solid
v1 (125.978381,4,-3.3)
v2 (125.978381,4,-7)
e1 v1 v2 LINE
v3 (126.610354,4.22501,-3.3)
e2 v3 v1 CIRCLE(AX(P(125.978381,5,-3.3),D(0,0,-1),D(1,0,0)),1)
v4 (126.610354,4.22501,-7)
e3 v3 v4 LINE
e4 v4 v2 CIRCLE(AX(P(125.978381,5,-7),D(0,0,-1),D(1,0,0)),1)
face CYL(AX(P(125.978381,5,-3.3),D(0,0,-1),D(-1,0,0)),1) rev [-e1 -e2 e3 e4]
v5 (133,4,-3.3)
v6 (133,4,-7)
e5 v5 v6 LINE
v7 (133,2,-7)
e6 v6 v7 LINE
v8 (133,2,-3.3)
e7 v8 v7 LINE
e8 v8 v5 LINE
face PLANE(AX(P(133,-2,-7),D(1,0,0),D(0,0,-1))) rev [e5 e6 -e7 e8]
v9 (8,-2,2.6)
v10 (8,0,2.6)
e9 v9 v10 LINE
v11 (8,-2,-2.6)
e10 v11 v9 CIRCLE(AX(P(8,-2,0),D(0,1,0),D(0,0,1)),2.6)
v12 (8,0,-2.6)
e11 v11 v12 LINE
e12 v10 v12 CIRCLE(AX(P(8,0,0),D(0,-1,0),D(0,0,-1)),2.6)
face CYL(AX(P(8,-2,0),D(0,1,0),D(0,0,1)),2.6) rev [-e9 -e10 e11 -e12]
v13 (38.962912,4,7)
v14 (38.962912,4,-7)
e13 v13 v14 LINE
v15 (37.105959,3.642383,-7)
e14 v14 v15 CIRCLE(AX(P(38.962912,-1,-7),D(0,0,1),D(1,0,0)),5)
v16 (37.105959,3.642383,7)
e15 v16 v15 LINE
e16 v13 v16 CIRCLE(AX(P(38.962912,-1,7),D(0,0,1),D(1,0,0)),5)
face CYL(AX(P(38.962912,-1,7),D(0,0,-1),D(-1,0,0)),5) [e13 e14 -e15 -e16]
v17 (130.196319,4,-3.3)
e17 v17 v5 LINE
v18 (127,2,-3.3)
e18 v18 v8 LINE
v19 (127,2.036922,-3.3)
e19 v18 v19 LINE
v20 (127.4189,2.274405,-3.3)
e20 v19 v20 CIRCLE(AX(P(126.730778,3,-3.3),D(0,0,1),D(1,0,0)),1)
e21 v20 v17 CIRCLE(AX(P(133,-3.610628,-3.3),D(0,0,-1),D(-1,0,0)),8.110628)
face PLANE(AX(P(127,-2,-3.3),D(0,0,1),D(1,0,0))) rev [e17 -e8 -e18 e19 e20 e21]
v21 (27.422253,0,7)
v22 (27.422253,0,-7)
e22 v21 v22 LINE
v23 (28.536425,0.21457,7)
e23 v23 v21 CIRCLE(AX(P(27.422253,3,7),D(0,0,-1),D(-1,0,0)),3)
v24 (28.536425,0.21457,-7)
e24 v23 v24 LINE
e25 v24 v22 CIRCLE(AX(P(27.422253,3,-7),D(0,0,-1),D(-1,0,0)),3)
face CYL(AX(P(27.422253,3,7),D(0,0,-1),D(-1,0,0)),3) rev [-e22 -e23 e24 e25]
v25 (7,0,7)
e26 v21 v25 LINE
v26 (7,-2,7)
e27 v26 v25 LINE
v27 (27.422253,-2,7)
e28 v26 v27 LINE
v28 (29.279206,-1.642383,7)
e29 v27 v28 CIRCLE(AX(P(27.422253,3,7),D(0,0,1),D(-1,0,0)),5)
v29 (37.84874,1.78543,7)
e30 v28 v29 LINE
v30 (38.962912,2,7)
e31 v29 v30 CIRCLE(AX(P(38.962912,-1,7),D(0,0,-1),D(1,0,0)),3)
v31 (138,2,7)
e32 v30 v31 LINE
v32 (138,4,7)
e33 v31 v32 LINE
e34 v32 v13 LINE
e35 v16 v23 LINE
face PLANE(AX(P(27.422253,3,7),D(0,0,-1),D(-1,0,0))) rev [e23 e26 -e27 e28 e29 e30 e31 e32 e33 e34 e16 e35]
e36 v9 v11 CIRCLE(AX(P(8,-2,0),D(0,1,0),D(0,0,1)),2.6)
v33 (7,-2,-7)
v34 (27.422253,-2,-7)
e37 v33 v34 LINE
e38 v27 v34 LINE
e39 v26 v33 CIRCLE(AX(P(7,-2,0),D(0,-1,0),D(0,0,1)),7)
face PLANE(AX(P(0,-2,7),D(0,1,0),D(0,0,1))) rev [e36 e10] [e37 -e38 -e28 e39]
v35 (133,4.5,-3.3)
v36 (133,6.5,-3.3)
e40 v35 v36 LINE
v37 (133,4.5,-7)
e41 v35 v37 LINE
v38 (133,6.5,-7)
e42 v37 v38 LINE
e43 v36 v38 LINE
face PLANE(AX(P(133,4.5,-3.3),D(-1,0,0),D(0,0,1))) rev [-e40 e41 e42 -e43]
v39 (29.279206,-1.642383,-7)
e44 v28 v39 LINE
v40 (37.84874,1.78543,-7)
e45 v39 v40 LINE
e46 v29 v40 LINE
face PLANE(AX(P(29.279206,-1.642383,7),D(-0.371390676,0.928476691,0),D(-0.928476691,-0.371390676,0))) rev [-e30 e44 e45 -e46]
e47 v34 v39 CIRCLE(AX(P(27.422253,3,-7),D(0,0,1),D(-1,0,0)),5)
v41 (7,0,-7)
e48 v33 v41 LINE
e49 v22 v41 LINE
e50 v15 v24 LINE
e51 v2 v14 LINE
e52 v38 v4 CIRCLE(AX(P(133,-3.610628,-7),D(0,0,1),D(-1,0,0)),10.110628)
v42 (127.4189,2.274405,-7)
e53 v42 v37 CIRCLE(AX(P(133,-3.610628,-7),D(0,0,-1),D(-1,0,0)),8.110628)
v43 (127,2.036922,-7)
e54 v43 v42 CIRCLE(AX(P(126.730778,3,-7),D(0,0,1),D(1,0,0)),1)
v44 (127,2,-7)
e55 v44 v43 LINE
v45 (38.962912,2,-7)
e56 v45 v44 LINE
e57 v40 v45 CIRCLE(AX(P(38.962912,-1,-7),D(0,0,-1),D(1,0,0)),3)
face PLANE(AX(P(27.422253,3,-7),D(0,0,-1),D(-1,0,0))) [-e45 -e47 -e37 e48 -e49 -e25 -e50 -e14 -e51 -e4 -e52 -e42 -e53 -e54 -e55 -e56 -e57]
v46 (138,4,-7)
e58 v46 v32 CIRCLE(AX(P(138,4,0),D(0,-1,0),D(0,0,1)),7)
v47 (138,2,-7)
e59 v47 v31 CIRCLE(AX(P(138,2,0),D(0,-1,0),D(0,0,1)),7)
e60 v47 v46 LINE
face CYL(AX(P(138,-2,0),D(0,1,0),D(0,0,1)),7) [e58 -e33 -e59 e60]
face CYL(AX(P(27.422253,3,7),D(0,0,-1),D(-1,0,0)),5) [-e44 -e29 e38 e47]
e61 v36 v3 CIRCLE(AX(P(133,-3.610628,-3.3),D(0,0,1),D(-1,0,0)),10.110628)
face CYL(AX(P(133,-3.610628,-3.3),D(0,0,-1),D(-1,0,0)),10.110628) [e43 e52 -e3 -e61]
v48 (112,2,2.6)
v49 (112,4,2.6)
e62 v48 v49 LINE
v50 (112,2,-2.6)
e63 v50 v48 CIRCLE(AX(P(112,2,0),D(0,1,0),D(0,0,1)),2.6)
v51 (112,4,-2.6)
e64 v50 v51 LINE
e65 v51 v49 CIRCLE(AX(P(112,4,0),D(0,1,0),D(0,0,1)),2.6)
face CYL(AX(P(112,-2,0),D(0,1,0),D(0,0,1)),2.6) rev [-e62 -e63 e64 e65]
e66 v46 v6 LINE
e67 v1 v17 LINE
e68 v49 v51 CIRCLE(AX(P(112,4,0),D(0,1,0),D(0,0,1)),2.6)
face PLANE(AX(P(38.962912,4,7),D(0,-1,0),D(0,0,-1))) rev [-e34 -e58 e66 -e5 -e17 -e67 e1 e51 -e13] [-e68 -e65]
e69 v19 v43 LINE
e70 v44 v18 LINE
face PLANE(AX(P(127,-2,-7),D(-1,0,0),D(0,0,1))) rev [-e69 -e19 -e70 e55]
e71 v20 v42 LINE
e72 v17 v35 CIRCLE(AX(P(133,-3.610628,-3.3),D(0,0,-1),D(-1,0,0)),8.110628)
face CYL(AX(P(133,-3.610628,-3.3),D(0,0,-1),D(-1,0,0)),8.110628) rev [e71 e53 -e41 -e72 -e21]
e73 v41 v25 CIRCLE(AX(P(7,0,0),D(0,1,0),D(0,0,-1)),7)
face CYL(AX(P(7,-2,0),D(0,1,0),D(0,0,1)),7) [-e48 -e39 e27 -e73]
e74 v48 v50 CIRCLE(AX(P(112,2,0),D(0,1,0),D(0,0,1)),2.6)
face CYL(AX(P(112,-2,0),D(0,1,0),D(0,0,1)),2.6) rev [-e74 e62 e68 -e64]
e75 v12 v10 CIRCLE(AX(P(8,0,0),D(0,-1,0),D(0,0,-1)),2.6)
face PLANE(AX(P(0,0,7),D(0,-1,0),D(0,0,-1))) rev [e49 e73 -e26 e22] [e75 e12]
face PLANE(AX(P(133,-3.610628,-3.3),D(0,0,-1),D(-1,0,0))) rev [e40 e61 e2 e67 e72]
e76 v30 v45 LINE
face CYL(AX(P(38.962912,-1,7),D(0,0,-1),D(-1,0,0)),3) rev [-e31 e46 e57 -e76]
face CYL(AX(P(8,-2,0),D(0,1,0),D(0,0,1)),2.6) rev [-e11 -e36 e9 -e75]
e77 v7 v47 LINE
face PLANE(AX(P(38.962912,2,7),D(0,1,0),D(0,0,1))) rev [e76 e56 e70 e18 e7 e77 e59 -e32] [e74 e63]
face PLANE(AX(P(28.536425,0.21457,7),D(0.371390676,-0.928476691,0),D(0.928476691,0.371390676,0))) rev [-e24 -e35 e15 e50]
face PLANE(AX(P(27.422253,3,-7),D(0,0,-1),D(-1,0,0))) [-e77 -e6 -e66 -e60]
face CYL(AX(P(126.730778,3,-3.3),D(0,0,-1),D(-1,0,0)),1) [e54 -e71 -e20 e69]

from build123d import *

# Parameters (mm, degrees)
EXTRUDE1_DEPTH      = 7
EXTRUDE2_DEPTH      = 146.223964964
EXTRUDE2_DEPTH_BACK = 146.223964964
SKETCH2_R           = 2.6
SKETCH5_W           = 6
SKETCH5_H           = 3.7
EXTRUDE5_DEPTH      = 146.292807805
EXTRUDE6_DEPTH      = 3.7


with BuildPart() as part:
    # Sketch1 → Extrude1 (new, symmetric)
    with BuildSketch(Plane.XY):
        with BuildLine():
            Line((0, 0), (27.422252789, 0))
            ThreePointArc((27.422252789, 0), (27.989575353, 0.05413084), (28.536424818, 0.214569927))
            Line((28.536424818, 0.214569927), (37.105958636, 3.642383454))
            ThreePointArc((37.105958636, 3.642383454), (38.017374412, 3.909781934), (38.962912018, 4))
            Line((38.962912018, 4), (145, 4))
            Line((145, 4), (145, 2))
            Line((145, 2), (38.962912018, 2))
            ThreePointArc((38.962912018, 2), (38.395589454, 1.94586916), (37.848739989, 1.785430073))
            Line((37.848739989, 1.785430073), (29.279206171, -1.642383454))
            ThreePointArc((29.279206171, -1.642383454), (28.367790395, -1.909781934), (27.422252789, -2))
            Line((27.422252789, -2), (0, -2))
            Line((0, -2), (0, 0))
        make_face()
    extrude(amount=EXTRUDE1_DEPTH, both=True)

    # Sketch2 → Extrude2 (cut, two sides: drawn at the far end of the back side and taken through both)
    with BuildSketch(Plane(origin=(0, 0, 0), x_dir=(1, 0, 0), z_dir=(0, 1, 0)).offset(-EXTRUDE2_DEPTH_BACK)):
        with Locations(Location((8, 0, 0), (0, 0, 270))):
            Circle(SKETCH2_R)
        with Locations(Location((112, 0, 0), (0, 0, 270))):
            Circle(SKETCH2_R)
        with BuildLine():
            Line((138, 7), (138, 13.502314884))
            Line((138, 13.502314884), (156.33198023, 13.502314884))
            Line((156.33198023, 13.502314884), (156.33198023, -14.26269046))
            Line((156.33198023, -14.26269046), (138, -14.26269046))
            Line((138, -14.26269046), (138, -7))
            ThreePointArc((138, -7), (145, 0), (138, 7))
        make_face()
        with BuildLine():
            Line((7, 7), (7, 12.663603668))
            Line((7, 12.663603668), (-7.097085647, 12.663603668))
            Line((-7.097085647, 12.663603668), (-7.097085647, -11.053510543))
            Line((-7.097085647, -11.053510543), (7, -11.053510543))
            Line((7, -11.053510543), (7, -7))
            ThreePointArc((7, -7), (0, 0), (7, 7))
        make_face()
    extrude(amount=EXTRUDE2_DEPTH + EXTRUDE2_DEPTH_BACK, mode=Mode.SUBTRACT)

    # Sketch5 → Extrude5 (cut, through all)
    with BuildSketch(Plane(origin=(0, 4, 0), x_dir=(1, 0, 0), z_dir=(0, 1, 0))):
        with Locations((130, 5.15)):
            Rectangle(SKETCH5_W, SKETCH5_H)
    extrude(amount=-EXTRUDE5_DEPTH, mode=Mode.SUBTRACT)

    # Sketch6 → Extrude6 (add)
    with BuildSketch(Plane.XY.offset(-7)):
        with BuildLine():
            Line((125.978380641, 4), (124.313573726, 4))
            Line((124.313573726, 4), (124.313573726, 2))
            Line((124.313573726, 2), (126.730778484, 2))
            ThreePointArc((126.730778484, 2), (127.10118691, 2.071131011), (127.418900283, 2.274404804))
            ThreePointArc((127.418900283, 2.274404804), (129.995755169, 3.923082851), (133, 4.5))
            Line((133, 4.5), (133, 6.5))
            ThreePointArc((133, 6.5), (129.608718605, 5.914287154), (126.61035388, 4.22500979))
            ThreePointArc((126.61035388, 4.22500979), (126.313798135, 4.057930414), (125.978380641, 4))
        make_face()
    extrude(amount=EXTRUDE6_DEPTH)


solid = part.part
